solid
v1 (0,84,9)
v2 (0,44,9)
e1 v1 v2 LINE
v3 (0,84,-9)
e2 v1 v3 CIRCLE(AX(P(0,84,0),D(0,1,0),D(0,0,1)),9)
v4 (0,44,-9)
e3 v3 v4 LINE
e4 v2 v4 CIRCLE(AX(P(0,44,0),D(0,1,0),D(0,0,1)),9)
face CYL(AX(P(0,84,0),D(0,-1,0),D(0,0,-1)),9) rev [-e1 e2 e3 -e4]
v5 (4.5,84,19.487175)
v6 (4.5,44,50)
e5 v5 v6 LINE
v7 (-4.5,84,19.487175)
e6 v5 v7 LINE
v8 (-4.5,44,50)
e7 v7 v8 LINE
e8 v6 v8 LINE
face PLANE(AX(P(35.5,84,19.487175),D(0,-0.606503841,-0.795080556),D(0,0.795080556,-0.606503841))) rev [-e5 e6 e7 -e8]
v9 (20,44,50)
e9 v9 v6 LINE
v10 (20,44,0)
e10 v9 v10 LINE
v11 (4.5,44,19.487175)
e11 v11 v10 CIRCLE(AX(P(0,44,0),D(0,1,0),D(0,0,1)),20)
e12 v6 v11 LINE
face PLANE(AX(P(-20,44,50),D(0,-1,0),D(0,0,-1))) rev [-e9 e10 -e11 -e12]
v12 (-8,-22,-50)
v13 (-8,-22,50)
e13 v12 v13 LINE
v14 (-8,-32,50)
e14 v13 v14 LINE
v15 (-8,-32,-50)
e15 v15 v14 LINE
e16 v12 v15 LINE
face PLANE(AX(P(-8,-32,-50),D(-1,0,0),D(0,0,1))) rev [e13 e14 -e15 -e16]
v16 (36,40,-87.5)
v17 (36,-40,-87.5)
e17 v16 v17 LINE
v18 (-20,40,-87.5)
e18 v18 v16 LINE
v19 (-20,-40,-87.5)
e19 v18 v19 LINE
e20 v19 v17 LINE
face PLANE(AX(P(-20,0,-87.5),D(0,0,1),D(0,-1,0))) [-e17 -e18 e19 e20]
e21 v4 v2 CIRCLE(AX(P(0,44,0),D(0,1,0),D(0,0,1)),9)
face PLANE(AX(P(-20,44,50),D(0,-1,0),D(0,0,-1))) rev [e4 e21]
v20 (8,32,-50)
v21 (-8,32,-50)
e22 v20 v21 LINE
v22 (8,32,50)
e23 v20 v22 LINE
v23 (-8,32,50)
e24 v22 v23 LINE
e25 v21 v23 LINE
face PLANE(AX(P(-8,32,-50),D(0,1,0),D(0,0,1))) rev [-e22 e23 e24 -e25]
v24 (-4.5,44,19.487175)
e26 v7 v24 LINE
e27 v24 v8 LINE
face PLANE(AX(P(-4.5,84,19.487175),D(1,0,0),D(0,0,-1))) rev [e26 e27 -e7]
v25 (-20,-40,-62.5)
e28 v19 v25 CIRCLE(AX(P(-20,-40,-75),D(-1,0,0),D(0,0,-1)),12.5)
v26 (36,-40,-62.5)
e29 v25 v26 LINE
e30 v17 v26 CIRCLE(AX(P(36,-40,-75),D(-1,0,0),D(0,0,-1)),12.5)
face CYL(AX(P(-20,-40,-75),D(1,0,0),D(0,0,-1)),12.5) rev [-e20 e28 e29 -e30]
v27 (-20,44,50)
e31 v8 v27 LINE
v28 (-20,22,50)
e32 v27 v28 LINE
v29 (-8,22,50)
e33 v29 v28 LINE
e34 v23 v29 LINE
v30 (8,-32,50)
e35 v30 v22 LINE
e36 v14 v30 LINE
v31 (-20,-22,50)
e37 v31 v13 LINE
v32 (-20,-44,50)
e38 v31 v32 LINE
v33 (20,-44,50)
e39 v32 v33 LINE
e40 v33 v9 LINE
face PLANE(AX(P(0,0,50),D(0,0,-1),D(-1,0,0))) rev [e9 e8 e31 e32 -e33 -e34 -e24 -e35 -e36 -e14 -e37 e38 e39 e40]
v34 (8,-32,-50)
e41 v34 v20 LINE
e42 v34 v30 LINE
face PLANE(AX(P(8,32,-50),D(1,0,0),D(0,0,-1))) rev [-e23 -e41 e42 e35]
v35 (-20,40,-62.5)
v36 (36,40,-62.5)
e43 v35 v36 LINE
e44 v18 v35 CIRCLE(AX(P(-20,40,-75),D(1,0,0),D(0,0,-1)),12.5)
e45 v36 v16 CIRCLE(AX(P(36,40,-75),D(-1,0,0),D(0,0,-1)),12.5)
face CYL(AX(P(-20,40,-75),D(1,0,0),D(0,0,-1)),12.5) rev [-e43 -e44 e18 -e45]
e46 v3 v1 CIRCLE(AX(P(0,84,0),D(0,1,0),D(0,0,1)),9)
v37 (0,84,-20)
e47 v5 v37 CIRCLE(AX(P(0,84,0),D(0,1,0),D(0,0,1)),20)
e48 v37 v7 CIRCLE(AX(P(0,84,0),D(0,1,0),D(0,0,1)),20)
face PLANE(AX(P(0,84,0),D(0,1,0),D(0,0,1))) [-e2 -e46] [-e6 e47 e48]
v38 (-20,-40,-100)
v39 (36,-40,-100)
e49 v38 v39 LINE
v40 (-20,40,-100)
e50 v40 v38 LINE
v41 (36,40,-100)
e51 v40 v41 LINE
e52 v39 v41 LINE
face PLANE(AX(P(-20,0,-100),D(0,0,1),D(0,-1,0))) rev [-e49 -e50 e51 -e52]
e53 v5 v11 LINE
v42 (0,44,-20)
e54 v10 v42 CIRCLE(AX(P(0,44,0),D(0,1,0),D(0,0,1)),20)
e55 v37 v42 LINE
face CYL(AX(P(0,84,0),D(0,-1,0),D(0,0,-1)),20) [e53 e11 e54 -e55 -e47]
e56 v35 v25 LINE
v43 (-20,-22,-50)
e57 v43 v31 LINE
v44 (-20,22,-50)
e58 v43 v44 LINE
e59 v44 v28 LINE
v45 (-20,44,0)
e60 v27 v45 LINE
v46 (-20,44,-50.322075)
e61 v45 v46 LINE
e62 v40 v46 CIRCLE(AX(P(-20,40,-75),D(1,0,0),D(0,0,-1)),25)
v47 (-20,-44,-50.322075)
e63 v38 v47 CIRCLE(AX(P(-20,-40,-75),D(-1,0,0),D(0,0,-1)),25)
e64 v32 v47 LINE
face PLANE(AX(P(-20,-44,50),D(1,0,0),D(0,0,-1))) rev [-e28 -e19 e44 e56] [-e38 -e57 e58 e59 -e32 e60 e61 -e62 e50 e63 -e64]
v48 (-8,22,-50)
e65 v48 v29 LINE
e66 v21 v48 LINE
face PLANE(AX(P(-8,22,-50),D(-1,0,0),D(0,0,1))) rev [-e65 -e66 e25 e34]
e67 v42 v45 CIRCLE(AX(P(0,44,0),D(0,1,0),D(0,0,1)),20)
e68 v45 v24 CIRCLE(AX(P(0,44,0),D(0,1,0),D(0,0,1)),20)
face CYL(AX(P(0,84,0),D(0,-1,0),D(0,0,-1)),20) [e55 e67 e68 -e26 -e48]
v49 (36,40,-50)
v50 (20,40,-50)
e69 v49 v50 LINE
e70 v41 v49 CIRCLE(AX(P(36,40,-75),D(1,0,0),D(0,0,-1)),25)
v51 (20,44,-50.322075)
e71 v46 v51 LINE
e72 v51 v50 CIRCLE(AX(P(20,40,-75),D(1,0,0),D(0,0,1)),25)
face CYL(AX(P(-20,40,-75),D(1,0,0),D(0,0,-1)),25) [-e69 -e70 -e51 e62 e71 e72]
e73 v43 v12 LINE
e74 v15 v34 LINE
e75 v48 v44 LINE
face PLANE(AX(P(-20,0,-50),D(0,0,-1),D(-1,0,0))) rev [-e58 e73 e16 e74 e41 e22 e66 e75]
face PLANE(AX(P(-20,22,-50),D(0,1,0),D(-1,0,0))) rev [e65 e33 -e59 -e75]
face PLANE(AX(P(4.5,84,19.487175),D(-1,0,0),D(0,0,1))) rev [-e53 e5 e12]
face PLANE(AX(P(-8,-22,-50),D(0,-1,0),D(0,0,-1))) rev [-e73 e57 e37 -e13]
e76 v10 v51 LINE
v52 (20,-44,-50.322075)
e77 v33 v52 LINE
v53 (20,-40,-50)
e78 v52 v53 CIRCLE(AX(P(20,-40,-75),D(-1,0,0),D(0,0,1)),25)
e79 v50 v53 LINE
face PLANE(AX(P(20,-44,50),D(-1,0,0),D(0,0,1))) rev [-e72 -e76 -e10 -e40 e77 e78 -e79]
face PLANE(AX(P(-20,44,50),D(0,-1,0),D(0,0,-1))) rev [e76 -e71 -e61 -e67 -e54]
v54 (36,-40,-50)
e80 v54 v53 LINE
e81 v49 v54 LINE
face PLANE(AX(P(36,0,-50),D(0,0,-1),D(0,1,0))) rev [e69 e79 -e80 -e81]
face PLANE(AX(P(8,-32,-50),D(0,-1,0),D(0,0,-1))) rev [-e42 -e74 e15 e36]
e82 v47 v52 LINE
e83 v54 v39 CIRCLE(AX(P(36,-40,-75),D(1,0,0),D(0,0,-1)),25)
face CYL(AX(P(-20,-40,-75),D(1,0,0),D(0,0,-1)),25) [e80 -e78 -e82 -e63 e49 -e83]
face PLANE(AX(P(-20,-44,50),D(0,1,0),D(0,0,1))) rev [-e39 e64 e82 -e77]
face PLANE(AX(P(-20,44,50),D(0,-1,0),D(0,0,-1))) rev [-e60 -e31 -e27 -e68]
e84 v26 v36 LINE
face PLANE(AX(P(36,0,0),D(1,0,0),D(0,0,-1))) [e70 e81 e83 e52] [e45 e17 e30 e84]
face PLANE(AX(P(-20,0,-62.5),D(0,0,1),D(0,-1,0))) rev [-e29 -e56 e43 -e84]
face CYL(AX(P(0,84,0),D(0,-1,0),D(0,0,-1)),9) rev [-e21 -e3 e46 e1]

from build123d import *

# Parameters (mm, degrees)
BASE_BLOCK_SKETCH_W         = 40
BASE_BLOCK_SKETCH_H         = 88
BASE_BLOCK_DEPTH            = 50
C_CHANNEL_CUT_DEPTH         = 112.067547015
SLOTTED_LUG_DEPTH           = 40
LUG_START                   = 16
LUG_RIM_DEPTH               = 16
BOSS_CYLINDER_SKETCH_18_R   = 20
BOSS_CYLINDER_SKETCH_18_R_2 = 9
BOSS_CYLINDER_18_DEPTH      = 40
BOSS_EXTENSION_DEPTH        = 40
BOSS_BORE_CUT_DEPTH         = 40
GUSSET_RIB_A_SKETCH_W       = 40
GUSSET_RIB_A_SKETCH_H       = 4
GUSSET_RIB_A_DEPTH          = 10
GUSSET_RIB_B_SKETCH_W       = 40
GUSSET_RIB_B_SKETCH_H       = 4
GUSSET_RIB_B_DEPTH          = 10


with BuildPart() as part:
    # Base Block Sketch → Base Block (new, symmetric)
    with BuildSketch(Plane.XY):
        Rectangle(BASE_BLOCK_SKETCH_W, BASE_BLOCK_SKETCH_H)
    extrude(amount=BASE_BLOCK_DEPTH, both=True)

    # C-Channel Cut Sketch → C-Channel Cut (cut, through all)
    with BuildSketch(Plane.XY.offset(50)):
        Polygon((-20, 22), (-8, 22), (-8, 32), (8, 32), (8, -32), (-8, -32), (-8, -22), (-20, -22), align=None)
    extrude(amount=-C_CHANNEL_CUT_DEPTH, mode=Mode.SUBTRACT)

    # Slotted Lug Sketch → Slotted Lug (add, through all)
    with BuildSketch(Plane(origin=(20, 0, 0), x_dir=(0, 0, -1), z_dir=(1, 0, 0))):
        with BuildLine():
            Line((100, -40), (100, 40))
            ThreePointArc((100, 40), (75, 65), (50, 40))
            Line((50, 40), (50, -40))
            ThreePointArc((50, -40), (75, -65), (100, -40))
        make_face()
        with BuildLine():
            Line((62.5, -40), (62.5, 40))
            ThreePointArc((62.5, 40), (75, 52.5), (87.5, 40))
            Line((87.5, 40), (87.5, -40))
            ThreePointArc((87.5, -40), (75, -52.5), (62.5, -40))
        make_face(mode=Mode.SUBTRACT)
    extrude(amount=-SLOTTED_LUG_DEPTH)

    # Lug Rim Sketch → Lug Rim (add)
    with BuildSketch(Plane(origin=(20, 0, 0), x_dir=(0, 0, -1), z_dir=(1, 0, 0)).offset(LUG_START)):
        with BuildLine():
            Line((50, 40), (50, -40))
            ThreePointArc((50, -40), (75, -65), (100, -40))
            Line((100, -40), (100, 40))
            ThreePointArc((100, 40), (75, 65), (50, 40))
        make_face()
        with BuildLine():
            ThreePointArc((62.5, 40), (75, 52.5), (87.5, 40))
            Line((87.5, 40), (87.5, -40))
            ThreePointArc((87.5, -40), (75, -52.5), (62.5, -40))
            Line((62.5, -40), (62.5, 40))
        make_face(mode=Mode.SUBTRACT)
    extrude(amount=-LUG_RIM_DEPTH)

    # Boss Cylinder Sketch Ø18 → Boss Cylinder Ø18 (add)
    with BuildSketch(Plane(origin=(0, 44, 0), x_dir=(1, 0, 0), z_dir=(0, 1, 0))):
        with Locations(Location((0, 0, 0), (0, 0, 180))):
            Circle(BOSS_CYLINDER_SKETCH_18_R)
        with Locations(Location((0, 0, 0), (0, 0, 270))):
            Circle(BOSS_CYLINDER_SKETCH_18_R_2, mode=Mode.SUBTRACT)
    extrude(amount=BOSS_CYLINDER_18_DEPTH)

    # Boss Extension Sketch → Boss Extension (add)
    with BuildSketch(Plane(origin=(0, 44, 0), x_dir=(1, 0, 0), z_dir=(0, 1, 0))):
        with BuildLine():
            Line((-4.5, -19.48717527), (-4.5, -50))
            Line((-4.5, -50), (4.5, -50))
            Line((4.5, -50), (4.5, -19.48717527))
            ThreePointArc((4.5, -19.48717527), (0, -20), (-4.5, -19.48717527))
        make_face()
    extrude(amount=BOSS_EXTENSION_DEPTH)

    # Boss Bore Sketch → Boss Bore Cut (cut)
    with BuildSketch(Plane.ZY.offset(4.5)):
        Polygon((19.48717527, 84), (50, 44), (50, 84), align=None)
    extrude(amount=-BOSS_BORE_CUT_DEPTH, mode=Mode.SUBTRACT)

    # Gusset Rib A Sketch → Gusset Rib A (add)
    with BuildSketch(Plane(origin=(0, 0, -50), x_dir=(-1, 0, 0), z_dir=(0, 0, -1))):
        with Locations((0, 42)):
            Rectangle(GUSSET_RIB_A_SKETCH_W, GUSSET_RIB_A_SKETCH_H)
    extrude(amount=GUSSET_RIB_A_DEPTH)

    # Gusset Rib B Sketch → Gusset Rib B (add)
    with BuildSketch(Plane(origin=(0, 0, -50), x_dir=(-1, 0, 0), z_dir=(0, 0, -1))):
        with Locations((0, -42)):
            Rectangle(GUSSET_RIB_B_SKETCH_W, GUSSET_RIB_B_SKETCH_H)
    extrude(amount=GUSSET_RIB_B_DEPTH)


solid = part.part
